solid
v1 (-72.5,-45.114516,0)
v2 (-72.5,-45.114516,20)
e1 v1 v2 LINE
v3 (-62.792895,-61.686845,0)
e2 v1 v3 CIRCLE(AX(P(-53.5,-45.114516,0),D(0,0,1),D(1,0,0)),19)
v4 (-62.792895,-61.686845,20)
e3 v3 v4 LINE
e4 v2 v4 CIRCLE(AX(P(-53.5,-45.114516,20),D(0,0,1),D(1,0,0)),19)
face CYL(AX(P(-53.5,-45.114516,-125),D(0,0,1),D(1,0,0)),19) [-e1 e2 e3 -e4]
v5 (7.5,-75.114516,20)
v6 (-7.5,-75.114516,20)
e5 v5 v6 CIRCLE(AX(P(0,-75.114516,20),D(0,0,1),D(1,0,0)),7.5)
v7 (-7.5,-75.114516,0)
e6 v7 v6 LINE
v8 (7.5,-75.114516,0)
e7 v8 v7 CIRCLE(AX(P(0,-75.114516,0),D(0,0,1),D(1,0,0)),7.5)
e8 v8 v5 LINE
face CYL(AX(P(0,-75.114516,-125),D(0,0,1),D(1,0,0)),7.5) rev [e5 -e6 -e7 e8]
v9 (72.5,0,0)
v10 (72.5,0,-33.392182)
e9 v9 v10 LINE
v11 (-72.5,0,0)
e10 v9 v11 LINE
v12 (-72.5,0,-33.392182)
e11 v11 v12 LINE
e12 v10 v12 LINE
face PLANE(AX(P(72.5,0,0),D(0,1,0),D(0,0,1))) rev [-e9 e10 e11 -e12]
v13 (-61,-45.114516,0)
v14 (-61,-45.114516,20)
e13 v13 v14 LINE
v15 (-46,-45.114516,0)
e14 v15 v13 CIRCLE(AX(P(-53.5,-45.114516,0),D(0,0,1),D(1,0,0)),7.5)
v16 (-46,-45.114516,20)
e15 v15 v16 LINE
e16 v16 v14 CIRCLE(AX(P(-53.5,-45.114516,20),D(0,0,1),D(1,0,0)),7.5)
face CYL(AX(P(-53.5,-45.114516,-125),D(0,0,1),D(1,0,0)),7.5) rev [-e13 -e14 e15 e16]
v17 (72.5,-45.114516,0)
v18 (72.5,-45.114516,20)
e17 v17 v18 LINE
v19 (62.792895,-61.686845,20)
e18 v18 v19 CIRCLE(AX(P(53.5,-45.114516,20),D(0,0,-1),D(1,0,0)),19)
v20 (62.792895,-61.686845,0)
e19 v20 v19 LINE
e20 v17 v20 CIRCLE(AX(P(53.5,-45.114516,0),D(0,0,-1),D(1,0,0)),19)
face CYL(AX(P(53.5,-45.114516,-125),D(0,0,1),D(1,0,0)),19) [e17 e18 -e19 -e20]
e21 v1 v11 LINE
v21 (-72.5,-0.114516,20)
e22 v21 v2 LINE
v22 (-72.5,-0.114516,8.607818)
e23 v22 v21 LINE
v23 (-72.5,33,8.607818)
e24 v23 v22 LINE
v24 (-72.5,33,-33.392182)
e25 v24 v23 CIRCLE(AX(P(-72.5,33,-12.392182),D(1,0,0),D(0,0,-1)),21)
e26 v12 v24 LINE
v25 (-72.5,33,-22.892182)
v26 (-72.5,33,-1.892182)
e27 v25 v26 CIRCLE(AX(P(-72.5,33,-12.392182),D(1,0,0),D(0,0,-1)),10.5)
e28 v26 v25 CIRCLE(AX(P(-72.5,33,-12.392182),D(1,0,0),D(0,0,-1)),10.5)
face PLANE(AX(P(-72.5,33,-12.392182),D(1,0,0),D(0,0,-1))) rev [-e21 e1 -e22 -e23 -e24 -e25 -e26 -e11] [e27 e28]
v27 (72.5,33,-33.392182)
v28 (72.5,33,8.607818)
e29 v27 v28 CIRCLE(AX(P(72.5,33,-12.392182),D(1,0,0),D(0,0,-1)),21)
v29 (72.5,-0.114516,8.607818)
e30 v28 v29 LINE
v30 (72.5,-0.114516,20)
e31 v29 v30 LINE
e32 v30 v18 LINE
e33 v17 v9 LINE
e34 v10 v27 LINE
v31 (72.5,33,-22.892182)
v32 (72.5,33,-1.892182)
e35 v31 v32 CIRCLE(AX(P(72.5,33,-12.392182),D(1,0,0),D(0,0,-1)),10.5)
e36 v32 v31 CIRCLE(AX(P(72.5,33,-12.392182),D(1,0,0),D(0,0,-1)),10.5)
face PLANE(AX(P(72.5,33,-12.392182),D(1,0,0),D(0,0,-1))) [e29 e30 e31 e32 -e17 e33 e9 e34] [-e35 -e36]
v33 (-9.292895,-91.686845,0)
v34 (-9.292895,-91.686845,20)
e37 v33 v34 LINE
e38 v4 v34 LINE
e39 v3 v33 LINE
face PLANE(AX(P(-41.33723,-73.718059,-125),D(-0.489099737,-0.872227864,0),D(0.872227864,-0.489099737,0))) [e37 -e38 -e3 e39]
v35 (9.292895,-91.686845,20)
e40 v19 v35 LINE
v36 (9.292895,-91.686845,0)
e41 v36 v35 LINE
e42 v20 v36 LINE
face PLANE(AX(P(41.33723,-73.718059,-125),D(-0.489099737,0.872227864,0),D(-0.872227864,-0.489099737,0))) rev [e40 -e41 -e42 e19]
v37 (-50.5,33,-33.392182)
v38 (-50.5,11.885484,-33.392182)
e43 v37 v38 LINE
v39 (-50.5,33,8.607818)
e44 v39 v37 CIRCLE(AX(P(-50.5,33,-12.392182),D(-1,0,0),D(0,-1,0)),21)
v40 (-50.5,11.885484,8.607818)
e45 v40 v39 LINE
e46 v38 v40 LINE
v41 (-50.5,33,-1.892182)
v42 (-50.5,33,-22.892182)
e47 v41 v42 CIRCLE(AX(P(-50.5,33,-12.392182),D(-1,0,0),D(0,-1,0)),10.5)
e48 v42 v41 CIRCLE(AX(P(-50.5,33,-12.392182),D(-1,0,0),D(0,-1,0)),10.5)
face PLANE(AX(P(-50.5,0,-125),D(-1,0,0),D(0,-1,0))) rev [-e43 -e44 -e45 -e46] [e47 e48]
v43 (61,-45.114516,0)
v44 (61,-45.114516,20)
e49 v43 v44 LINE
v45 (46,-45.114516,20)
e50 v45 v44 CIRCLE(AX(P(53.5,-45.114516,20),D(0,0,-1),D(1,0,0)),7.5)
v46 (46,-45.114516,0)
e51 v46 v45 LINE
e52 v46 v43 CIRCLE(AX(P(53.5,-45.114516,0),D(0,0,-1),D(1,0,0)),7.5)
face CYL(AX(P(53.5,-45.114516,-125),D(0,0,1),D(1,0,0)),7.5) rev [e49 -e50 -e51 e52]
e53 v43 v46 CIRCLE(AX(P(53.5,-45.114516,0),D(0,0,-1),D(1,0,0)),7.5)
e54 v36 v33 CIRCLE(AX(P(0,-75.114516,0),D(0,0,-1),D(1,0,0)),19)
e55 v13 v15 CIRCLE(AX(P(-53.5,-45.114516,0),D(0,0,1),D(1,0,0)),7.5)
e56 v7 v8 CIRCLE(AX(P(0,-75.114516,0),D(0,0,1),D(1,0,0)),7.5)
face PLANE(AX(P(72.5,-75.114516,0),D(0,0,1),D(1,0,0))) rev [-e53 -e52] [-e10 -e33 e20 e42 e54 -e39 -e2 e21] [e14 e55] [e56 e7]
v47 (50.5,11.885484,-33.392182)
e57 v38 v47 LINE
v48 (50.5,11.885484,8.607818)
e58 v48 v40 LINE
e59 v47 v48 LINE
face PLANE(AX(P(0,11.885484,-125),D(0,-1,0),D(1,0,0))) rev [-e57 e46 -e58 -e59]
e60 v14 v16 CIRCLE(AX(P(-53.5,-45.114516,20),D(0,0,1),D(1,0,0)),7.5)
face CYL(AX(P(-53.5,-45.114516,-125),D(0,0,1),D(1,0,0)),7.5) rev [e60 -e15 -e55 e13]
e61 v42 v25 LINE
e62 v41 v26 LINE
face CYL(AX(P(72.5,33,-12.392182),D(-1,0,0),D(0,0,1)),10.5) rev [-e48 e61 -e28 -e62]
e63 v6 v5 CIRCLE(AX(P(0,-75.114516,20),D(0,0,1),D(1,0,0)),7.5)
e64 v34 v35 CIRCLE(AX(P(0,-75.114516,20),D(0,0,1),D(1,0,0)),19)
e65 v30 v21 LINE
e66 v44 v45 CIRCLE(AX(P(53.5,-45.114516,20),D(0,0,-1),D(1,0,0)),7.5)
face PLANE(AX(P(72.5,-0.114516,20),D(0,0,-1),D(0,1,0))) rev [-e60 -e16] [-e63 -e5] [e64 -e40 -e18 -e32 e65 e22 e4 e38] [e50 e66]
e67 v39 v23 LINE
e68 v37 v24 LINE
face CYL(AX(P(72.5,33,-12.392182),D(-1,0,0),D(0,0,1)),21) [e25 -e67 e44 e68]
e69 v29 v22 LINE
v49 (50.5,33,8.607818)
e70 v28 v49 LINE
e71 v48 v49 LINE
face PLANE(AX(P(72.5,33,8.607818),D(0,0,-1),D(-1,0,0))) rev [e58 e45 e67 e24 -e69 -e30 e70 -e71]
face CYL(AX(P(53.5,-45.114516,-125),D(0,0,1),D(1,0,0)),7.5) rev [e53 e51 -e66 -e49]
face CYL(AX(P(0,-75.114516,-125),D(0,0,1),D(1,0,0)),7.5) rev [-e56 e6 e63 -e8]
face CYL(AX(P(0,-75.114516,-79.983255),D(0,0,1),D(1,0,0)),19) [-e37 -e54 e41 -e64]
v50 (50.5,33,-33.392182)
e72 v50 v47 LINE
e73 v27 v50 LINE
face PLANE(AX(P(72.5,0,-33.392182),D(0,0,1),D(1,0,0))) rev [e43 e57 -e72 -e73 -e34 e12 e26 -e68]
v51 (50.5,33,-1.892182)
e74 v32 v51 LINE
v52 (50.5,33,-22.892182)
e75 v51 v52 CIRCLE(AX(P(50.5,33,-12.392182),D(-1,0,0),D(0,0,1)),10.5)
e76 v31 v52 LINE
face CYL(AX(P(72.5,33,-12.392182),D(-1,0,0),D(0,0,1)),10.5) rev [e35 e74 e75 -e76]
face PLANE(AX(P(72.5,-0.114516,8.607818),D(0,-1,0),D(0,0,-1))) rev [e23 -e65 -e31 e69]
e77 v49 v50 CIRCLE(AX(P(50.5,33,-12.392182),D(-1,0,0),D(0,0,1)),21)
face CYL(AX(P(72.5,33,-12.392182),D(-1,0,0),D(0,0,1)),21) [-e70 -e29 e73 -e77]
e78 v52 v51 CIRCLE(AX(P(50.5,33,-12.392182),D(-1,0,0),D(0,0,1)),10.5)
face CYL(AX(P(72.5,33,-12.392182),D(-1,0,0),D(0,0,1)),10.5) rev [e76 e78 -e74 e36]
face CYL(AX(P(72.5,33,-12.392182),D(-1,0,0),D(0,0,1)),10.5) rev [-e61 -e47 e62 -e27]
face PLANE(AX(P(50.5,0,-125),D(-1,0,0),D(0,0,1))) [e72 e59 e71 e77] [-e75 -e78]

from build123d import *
from build123d.topology import SkipClean

# Parameters (mm, degrees)
BRACKET_PROFILE_SKETCH_R       = 10.5
BRACKET_BODY_145MM_DEPTH       = 72.5
PLATE_AND_LUG_OUTLINE_SKETCH_R = 7.5
PLATE_AND_LUG_OUTLINE_SKETCH_W = 101
PLATE_AND_LUG_OUTLINE_SKETCH_H = 63.401381975
OUTLINE_AND_HOLES_CUT_DEPTH    = 145
LUG_REGION_BOSS_DEPTH          = 20


with BuildPart() as part:
    # Bracket Profile Sketch → Bracket Body 145mm (new, symmetric)
    with BuildSketch(Plane(origin=(0, 0, 0), x_dir=(0, 0, -1), z_dir=(1, 0, 0))):
        with BuildLine():
            Line((-8.607818135, 33), (-8.607818135, -0.114515686))
            Line((-8.607818135, -0.114515686), (-20, -0.114515686))
            Line((-20, -0.114515686), (-20, -75.114515686))
            Line((-20, -75.114515686), (0, -75.114515686))
            Line((0, -75.114515686), (0, 0))
            Line((0, 0), (33.392181865, 0))
            Line((33.392181865, 0), (33.392181865, 33))
            ThreePointArc((33.392181865, 33), (12.392181865, 54), (-8.607818135, 33))
        make_face()
        with Locations((12.392181865, 33)):
            Circle(BRACKET_PROFILE_SKETCH_R, mode=Mode.SUBTRACT)
    extrude(amount=BRACKET_BODY_145MM_DEPTH, both=True)

    # Plate and Lug Outline Sketch → Outline and Holes Cut (cut)
    with BuildSketch(Plane.XY.offset(20)):
        with BuildLine():
            Line((-38.846882472, -75.114515686), (-62.792895003, -61.686845107))
            ThreePointArc((-62.792895003, -61.686845107), (-69.894587599, -54.717509879), (-72.5, -45.114515686))
            Line((-72.5, -45.114515686), (-72.5, -75.114515686))
            Line((-72.5, -75.114515686), (-38.846882472, -75.114515686))
        make_face()
        with BuildLine():
            Line((62.792895003, -61.686845107), (38.846882472, -75.114515686))
            Line((38.846882472, -75.114515686), (72.5, -75.114515686))
            Line((72.5, -75.114515686), (72.5, -45.114515686))
            ThreePointArc((72.5, -45.114515686), (69.894587599, -54.717509879), (62.792895003, -61.686845107))
        make_face()
        with Locations((53.5, -45.114515686)):
            Circle(PLATE_AND_LUG_OUTLINE_SKETCH_R)
        with BuildLine():
            ThreePointArc((0, -67.614515686), (-5.303300859, -69.811214827), (-7.5, -75.114515686))
            Line((-7.5, -75.114515686), (0, -75.114515686))
            Line((0, -75.114515686), (0, -67.614515686))
        make_face()
        with BuildLine():
            ThreePointArc((7.5, -75.114515686), (5.303300859, -69.811214827), (0, -67.614515686))
            Line((0, -67.614515686), (0, -75.114515686))
            Line((0, -75.114515686), (7.5, -75.114515686))
        make_face()
        with BuildLine():
            Line((0, -75.114515686), (-7.5, -75.114515686))
            ThreePointArc((-7.5, -75.114515686), (0, -82.614515686), (7.5, -75.114515686))
            Line((7.5, -75.114515686), (0, -75.114515686))
        make_face()
        with Locations((-53.5, -45.114515686)):
            Circle(PLATE_AND_LUG_OUTLINE_SKETCH_R)
        with Locations((0, 43.586175301)):
            Rectangle(PLATE_AND_LUG_OUTLINE_SKETCH_W, PLATE_AND_LUG_OUTLINE_SKETCH_H)
    extrude(amount=-OUTLINE_AND_HOLES_CUT_DEPTH, mode=Mode.SUBTRACT)

    # Sketch2_3 → Lug Region Boss (add)
    with SkipClean():  # the faces are left unmerged after this step: merging them gives an invalid solid
        with BuildSketch(Plane.XY.offset(20)):
            with BuildLine():
                Line((-7.5, -75.114515686), (-38.846882472, -75.114515686))
                Line((-38.846882472, -75.114515686), (-9.292895003, -91.686845107))
                ThreePointArc((-9.292895003, -91.686845107), (0, -94.114515686), (9.292895003, -91.686845107))
                Line((9.292895003, -91.686845107), (38.846882472, -75.114515686))
                Line((38.846882472, -75.114515686), (7.5, -75.114515686))
                ThreePointArc((7.5, -75.114515686), (0, -82.614515686), (-7.5, -75.114515686))
            make_face()
        extrude(amount=-LUG_REGION_BOSS_DEPTH)


solid = part.part
